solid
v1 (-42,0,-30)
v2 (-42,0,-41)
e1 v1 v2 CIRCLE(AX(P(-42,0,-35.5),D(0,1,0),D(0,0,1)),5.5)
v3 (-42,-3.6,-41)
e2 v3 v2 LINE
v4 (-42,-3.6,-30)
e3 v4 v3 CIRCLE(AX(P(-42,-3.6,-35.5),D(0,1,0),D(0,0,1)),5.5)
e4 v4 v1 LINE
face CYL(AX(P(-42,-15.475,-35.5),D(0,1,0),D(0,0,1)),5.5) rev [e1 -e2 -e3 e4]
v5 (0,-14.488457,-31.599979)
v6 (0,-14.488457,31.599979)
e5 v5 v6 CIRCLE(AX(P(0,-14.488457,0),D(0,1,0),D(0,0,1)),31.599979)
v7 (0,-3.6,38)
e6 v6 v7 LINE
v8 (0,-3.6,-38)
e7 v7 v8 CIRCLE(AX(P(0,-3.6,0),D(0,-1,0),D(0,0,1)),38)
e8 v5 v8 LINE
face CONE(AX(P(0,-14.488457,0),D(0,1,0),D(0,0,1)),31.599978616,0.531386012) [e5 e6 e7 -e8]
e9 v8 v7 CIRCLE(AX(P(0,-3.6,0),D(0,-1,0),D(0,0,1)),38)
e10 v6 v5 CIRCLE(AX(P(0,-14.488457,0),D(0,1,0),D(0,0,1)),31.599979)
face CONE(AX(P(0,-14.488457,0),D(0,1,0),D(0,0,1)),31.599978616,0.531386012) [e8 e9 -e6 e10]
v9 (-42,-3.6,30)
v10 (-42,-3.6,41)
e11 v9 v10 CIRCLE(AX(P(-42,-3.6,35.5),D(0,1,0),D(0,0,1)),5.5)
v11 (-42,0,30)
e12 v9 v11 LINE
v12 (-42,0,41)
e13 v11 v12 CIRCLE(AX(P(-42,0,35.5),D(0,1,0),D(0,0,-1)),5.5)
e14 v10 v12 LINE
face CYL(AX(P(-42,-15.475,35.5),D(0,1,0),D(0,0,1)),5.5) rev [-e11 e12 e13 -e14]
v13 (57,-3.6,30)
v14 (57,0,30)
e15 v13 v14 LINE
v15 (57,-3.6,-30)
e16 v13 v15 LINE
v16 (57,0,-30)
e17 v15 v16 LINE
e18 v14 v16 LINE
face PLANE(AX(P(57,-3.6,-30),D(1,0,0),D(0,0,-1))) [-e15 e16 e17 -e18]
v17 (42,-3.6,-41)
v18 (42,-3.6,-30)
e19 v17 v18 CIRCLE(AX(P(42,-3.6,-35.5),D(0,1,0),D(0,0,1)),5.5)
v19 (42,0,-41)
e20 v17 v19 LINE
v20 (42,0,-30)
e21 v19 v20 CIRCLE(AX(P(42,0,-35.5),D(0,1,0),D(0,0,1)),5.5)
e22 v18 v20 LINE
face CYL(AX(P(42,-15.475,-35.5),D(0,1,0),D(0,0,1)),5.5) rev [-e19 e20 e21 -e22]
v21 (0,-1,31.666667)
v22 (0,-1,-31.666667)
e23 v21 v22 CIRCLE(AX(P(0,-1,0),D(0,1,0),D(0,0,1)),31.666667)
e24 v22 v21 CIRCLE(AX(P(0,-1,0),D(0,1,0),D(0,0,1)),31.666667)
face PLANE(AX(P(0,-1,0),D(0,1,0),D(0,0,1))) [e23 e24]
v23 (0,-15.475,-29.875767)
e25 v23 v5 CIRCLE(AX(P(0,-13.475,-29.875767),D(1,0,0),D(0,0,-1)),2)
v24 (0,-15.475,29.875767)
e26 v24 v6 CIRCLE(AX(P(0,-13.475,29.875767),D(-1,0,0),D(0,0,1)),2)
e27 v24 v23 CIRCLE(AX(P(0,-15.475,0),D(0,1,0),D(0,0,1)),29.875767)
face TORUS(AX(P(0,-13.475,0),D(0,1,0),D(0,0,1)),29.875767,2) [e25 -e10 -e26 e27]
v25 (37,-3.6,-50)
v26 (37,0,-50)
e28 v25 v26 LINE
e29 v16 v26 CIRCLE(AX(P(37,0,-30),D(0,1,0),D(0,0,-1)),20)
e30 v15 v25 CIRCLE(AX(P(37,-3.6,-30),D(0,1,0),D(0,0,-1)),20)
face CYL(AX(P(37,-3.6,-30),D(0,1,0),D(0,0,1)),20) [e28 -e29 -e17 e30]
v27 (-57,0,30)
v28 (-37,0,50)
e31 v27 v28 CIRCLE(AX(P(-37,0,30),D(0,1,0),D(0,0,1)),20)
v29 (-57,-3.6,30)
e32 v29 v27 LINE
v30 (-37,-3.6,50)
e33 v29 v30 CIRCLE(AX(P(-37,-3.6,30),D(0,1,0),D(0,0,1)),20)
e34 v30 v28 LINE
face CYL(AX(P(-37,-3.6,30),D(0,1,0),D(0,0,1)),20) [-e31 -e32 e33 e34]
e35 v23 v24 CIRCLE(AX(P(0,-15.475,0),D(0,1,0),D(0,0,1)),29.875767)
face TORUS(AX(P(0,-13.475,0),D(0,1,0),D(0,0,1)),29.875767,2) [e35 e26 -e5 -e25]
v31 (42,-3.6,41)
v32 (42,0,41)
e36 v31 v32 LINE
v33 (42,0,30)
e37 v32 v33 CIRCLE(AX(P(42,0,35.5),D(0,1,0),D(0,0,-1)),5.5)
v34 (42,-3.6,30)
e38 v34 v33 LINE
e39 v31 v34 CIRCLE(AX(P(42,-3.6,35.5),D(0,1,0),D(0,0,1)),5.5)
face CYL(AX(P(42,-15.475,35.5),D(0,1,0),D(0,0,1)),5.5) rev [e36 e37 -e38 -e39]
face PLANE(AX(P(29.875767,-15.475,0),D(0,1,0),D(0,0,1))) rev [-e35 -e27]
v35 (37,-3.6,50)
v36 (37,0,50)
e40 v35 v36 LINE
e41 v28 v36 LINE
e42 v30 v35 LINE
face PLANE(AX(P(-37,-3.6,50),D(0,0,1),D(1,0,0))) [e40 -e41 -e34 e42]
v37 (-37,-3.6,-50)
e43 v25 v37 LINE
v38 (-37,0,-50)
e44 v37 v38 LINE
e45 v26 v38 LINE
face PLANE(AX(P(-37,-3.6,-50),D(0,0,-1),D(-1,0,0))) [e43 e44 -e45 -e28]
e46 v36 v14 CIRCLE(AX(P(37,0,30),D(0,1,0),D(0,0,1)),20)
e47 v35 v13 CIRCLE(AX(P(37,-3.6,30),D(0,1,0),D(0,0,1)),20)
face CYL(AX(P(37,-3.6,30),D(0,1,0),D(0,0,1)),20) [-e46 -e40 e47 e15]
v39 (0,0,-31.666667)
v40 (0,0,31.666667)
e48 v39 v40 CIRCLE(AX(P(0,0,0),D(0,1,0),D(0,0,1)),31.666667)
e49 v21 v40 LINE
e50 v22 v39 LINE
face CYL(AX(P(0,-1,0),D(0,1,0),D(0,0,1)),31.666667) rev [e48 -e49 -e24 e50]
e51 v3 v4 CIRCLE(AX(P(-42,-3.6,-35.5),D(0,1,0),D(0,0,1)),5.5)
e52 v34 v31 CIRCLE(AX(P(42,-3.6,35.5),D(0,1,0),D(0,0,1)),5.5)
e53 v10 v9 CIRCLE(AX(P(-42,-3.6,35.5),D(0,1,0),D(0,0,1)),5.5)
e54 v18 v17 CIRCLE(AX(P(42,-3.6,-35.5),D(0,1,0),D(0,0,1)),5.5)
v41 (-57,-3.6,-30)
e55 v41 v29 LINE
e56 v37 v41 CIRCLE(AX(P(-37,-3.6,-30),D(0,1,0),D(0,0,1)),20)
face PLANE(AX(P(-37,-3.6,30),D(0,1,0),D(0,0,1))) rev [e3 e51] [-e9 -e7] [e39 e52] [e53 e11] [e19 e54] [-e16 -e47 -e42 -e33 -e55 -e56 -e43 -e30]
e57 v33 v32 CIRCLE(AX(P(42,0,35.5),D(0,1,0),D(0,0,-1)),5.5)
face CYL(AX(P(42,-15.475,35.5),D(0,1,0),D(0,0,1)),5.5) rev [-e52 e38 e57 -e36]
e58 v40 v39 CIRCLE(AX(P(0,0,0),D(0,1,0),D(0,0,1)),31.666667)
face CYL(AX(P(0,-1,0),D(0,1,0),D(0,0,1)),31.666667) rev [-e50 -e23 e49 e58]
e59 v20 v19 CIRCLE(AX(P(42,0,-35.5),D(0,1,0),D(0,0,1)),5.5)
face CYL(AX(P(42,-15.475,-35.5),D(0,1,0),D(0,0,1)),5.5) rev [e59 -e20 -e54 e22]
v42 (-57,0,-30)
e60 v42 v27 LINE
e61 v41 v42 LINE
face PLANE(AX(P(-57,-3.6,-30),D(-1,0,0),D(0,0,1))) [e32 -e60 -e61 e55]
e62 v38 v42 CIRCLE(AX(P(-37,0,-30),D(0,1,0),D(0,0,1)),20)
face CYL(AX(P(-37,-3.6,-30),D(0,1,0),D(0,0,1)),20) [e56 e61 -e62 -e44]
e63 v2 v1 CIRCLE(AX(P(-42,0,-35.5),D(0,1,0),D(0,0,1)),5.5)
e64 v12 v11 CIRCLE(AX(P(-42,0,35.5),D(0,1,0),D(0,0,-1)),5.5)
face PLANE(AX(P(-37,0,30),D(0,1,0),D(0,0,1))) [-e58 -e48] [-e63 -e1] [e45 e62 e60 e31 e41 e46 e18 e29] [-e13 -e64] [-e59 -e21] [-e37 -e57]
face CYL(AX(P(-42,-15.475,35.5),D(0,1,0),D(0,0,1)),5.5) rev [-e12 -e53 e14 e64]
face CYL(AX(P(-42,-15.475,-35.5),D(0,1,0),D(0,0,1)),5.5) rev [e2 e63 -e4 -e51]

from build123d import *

# Parameters (mm, degrees)
BOSS_EXTRUDE1_DEPTH = 3.6
SKETCH2_R           = 31.666666667
CUT_EXTRUDE1_DEPTH  = 1
SKETCH4_R           = 5.5
CUT_EXTRUDE2_DEPTH  = 78.385241649


with BuildPart() as part:
    # Sketch1 → Boss-Extrude1 (new body)
    with BuildSketch(Plane(origin=(0, 0, 0), x_dir=(1, 0, 0), z_dir=(0, 1, 0))):
        with BuildLine():
            Line((-37, 50), (37, 50))
            ThreePointArc((37, 50), (51.142135624, 44.142135624), (57, 30))
            Line((57, 30), (57, -30))
            ThreePointArc((57, -30), (51.142135624, -44.142135624), (37, -50))
            Line((37, -50), (-37, -50))
            ThreePointArc((-37, -50), (-51.142135624, -44.142135624), (-57, -30))
            Line((-57, -30), (-57, 30))
            ThreePointArc((-57, 30), (-51.142135624, 44.142135624), (-37, 50))
        make_face()
    extrude(amount=-BOSS_EXTRUDE1_DEPTH)

    # Sketch2 → Cut-Extrude1 (cut)
    with BuildSketch(Plane(origin=(0, 0, 0), x_dir=(1, 0, 0), z_dir=(0, 1, 0))):
        with Locations(Location((0, 0, 0), (0, 0, 270))):
            Circle(SKETCH2_R)
    extrude(amount=-CUT_EXTRUDE1_DEPTH, mode=Mode.SUBTRACT)

    # Sketch3 → Revolve1 (revolve)
    with BuildSketch(Plane.XY, mode=Mode.PRIVATE) as revolve1_sk:
        with BuildLine():
            Line((0, -3.6), (38, -3.6))
            Line((38, -3.6), (31.599978616, -14.488457433))
            ThreePointArc((31.599978616, -14.488457433), (30.869015975, -15.210931287), (29.875767483, -15.475))
            Line((29.875767483, -15.475), (0, -15.475))
            Line((0, -15.475), (0, -3.6))
        make_face()
    revolve(revolve1_sk.sketch.rotate(Axis((0, -15.475, 0), (0, 1, 0)), 270), axis=Axis((0, -15.475, 0), (0, 1, 0)))

    # Sketch4 → Cut-Extrude2 (cut, through all)
    with BuildSketch(Plane(origin=(0, 0, 0), x_dir=(1, 0, 0), z_dir=(0, 1, 0))):
        with Locations(Location((-42, 35.5, 0), (0, 0, 270))):
            Circle(SKETCH4_R)
        with Locations(Location((42, 35.5, 0), (0, 0, 270))):
            Circle(SKETCH4_R)
        with Locations(Location((42, -35.5, 0), (0, 0, 270))):
            Circle(SKETCH4_R)
        with Locations(Location((-42, -35.5, 0), (0, 0, 270))):
            Circle(SKETCH4_R)
    extrude(amount=-CUT_EXTRUDE2_DEPTH, mode=Mode.SUBTRACT)


solid = part.part
